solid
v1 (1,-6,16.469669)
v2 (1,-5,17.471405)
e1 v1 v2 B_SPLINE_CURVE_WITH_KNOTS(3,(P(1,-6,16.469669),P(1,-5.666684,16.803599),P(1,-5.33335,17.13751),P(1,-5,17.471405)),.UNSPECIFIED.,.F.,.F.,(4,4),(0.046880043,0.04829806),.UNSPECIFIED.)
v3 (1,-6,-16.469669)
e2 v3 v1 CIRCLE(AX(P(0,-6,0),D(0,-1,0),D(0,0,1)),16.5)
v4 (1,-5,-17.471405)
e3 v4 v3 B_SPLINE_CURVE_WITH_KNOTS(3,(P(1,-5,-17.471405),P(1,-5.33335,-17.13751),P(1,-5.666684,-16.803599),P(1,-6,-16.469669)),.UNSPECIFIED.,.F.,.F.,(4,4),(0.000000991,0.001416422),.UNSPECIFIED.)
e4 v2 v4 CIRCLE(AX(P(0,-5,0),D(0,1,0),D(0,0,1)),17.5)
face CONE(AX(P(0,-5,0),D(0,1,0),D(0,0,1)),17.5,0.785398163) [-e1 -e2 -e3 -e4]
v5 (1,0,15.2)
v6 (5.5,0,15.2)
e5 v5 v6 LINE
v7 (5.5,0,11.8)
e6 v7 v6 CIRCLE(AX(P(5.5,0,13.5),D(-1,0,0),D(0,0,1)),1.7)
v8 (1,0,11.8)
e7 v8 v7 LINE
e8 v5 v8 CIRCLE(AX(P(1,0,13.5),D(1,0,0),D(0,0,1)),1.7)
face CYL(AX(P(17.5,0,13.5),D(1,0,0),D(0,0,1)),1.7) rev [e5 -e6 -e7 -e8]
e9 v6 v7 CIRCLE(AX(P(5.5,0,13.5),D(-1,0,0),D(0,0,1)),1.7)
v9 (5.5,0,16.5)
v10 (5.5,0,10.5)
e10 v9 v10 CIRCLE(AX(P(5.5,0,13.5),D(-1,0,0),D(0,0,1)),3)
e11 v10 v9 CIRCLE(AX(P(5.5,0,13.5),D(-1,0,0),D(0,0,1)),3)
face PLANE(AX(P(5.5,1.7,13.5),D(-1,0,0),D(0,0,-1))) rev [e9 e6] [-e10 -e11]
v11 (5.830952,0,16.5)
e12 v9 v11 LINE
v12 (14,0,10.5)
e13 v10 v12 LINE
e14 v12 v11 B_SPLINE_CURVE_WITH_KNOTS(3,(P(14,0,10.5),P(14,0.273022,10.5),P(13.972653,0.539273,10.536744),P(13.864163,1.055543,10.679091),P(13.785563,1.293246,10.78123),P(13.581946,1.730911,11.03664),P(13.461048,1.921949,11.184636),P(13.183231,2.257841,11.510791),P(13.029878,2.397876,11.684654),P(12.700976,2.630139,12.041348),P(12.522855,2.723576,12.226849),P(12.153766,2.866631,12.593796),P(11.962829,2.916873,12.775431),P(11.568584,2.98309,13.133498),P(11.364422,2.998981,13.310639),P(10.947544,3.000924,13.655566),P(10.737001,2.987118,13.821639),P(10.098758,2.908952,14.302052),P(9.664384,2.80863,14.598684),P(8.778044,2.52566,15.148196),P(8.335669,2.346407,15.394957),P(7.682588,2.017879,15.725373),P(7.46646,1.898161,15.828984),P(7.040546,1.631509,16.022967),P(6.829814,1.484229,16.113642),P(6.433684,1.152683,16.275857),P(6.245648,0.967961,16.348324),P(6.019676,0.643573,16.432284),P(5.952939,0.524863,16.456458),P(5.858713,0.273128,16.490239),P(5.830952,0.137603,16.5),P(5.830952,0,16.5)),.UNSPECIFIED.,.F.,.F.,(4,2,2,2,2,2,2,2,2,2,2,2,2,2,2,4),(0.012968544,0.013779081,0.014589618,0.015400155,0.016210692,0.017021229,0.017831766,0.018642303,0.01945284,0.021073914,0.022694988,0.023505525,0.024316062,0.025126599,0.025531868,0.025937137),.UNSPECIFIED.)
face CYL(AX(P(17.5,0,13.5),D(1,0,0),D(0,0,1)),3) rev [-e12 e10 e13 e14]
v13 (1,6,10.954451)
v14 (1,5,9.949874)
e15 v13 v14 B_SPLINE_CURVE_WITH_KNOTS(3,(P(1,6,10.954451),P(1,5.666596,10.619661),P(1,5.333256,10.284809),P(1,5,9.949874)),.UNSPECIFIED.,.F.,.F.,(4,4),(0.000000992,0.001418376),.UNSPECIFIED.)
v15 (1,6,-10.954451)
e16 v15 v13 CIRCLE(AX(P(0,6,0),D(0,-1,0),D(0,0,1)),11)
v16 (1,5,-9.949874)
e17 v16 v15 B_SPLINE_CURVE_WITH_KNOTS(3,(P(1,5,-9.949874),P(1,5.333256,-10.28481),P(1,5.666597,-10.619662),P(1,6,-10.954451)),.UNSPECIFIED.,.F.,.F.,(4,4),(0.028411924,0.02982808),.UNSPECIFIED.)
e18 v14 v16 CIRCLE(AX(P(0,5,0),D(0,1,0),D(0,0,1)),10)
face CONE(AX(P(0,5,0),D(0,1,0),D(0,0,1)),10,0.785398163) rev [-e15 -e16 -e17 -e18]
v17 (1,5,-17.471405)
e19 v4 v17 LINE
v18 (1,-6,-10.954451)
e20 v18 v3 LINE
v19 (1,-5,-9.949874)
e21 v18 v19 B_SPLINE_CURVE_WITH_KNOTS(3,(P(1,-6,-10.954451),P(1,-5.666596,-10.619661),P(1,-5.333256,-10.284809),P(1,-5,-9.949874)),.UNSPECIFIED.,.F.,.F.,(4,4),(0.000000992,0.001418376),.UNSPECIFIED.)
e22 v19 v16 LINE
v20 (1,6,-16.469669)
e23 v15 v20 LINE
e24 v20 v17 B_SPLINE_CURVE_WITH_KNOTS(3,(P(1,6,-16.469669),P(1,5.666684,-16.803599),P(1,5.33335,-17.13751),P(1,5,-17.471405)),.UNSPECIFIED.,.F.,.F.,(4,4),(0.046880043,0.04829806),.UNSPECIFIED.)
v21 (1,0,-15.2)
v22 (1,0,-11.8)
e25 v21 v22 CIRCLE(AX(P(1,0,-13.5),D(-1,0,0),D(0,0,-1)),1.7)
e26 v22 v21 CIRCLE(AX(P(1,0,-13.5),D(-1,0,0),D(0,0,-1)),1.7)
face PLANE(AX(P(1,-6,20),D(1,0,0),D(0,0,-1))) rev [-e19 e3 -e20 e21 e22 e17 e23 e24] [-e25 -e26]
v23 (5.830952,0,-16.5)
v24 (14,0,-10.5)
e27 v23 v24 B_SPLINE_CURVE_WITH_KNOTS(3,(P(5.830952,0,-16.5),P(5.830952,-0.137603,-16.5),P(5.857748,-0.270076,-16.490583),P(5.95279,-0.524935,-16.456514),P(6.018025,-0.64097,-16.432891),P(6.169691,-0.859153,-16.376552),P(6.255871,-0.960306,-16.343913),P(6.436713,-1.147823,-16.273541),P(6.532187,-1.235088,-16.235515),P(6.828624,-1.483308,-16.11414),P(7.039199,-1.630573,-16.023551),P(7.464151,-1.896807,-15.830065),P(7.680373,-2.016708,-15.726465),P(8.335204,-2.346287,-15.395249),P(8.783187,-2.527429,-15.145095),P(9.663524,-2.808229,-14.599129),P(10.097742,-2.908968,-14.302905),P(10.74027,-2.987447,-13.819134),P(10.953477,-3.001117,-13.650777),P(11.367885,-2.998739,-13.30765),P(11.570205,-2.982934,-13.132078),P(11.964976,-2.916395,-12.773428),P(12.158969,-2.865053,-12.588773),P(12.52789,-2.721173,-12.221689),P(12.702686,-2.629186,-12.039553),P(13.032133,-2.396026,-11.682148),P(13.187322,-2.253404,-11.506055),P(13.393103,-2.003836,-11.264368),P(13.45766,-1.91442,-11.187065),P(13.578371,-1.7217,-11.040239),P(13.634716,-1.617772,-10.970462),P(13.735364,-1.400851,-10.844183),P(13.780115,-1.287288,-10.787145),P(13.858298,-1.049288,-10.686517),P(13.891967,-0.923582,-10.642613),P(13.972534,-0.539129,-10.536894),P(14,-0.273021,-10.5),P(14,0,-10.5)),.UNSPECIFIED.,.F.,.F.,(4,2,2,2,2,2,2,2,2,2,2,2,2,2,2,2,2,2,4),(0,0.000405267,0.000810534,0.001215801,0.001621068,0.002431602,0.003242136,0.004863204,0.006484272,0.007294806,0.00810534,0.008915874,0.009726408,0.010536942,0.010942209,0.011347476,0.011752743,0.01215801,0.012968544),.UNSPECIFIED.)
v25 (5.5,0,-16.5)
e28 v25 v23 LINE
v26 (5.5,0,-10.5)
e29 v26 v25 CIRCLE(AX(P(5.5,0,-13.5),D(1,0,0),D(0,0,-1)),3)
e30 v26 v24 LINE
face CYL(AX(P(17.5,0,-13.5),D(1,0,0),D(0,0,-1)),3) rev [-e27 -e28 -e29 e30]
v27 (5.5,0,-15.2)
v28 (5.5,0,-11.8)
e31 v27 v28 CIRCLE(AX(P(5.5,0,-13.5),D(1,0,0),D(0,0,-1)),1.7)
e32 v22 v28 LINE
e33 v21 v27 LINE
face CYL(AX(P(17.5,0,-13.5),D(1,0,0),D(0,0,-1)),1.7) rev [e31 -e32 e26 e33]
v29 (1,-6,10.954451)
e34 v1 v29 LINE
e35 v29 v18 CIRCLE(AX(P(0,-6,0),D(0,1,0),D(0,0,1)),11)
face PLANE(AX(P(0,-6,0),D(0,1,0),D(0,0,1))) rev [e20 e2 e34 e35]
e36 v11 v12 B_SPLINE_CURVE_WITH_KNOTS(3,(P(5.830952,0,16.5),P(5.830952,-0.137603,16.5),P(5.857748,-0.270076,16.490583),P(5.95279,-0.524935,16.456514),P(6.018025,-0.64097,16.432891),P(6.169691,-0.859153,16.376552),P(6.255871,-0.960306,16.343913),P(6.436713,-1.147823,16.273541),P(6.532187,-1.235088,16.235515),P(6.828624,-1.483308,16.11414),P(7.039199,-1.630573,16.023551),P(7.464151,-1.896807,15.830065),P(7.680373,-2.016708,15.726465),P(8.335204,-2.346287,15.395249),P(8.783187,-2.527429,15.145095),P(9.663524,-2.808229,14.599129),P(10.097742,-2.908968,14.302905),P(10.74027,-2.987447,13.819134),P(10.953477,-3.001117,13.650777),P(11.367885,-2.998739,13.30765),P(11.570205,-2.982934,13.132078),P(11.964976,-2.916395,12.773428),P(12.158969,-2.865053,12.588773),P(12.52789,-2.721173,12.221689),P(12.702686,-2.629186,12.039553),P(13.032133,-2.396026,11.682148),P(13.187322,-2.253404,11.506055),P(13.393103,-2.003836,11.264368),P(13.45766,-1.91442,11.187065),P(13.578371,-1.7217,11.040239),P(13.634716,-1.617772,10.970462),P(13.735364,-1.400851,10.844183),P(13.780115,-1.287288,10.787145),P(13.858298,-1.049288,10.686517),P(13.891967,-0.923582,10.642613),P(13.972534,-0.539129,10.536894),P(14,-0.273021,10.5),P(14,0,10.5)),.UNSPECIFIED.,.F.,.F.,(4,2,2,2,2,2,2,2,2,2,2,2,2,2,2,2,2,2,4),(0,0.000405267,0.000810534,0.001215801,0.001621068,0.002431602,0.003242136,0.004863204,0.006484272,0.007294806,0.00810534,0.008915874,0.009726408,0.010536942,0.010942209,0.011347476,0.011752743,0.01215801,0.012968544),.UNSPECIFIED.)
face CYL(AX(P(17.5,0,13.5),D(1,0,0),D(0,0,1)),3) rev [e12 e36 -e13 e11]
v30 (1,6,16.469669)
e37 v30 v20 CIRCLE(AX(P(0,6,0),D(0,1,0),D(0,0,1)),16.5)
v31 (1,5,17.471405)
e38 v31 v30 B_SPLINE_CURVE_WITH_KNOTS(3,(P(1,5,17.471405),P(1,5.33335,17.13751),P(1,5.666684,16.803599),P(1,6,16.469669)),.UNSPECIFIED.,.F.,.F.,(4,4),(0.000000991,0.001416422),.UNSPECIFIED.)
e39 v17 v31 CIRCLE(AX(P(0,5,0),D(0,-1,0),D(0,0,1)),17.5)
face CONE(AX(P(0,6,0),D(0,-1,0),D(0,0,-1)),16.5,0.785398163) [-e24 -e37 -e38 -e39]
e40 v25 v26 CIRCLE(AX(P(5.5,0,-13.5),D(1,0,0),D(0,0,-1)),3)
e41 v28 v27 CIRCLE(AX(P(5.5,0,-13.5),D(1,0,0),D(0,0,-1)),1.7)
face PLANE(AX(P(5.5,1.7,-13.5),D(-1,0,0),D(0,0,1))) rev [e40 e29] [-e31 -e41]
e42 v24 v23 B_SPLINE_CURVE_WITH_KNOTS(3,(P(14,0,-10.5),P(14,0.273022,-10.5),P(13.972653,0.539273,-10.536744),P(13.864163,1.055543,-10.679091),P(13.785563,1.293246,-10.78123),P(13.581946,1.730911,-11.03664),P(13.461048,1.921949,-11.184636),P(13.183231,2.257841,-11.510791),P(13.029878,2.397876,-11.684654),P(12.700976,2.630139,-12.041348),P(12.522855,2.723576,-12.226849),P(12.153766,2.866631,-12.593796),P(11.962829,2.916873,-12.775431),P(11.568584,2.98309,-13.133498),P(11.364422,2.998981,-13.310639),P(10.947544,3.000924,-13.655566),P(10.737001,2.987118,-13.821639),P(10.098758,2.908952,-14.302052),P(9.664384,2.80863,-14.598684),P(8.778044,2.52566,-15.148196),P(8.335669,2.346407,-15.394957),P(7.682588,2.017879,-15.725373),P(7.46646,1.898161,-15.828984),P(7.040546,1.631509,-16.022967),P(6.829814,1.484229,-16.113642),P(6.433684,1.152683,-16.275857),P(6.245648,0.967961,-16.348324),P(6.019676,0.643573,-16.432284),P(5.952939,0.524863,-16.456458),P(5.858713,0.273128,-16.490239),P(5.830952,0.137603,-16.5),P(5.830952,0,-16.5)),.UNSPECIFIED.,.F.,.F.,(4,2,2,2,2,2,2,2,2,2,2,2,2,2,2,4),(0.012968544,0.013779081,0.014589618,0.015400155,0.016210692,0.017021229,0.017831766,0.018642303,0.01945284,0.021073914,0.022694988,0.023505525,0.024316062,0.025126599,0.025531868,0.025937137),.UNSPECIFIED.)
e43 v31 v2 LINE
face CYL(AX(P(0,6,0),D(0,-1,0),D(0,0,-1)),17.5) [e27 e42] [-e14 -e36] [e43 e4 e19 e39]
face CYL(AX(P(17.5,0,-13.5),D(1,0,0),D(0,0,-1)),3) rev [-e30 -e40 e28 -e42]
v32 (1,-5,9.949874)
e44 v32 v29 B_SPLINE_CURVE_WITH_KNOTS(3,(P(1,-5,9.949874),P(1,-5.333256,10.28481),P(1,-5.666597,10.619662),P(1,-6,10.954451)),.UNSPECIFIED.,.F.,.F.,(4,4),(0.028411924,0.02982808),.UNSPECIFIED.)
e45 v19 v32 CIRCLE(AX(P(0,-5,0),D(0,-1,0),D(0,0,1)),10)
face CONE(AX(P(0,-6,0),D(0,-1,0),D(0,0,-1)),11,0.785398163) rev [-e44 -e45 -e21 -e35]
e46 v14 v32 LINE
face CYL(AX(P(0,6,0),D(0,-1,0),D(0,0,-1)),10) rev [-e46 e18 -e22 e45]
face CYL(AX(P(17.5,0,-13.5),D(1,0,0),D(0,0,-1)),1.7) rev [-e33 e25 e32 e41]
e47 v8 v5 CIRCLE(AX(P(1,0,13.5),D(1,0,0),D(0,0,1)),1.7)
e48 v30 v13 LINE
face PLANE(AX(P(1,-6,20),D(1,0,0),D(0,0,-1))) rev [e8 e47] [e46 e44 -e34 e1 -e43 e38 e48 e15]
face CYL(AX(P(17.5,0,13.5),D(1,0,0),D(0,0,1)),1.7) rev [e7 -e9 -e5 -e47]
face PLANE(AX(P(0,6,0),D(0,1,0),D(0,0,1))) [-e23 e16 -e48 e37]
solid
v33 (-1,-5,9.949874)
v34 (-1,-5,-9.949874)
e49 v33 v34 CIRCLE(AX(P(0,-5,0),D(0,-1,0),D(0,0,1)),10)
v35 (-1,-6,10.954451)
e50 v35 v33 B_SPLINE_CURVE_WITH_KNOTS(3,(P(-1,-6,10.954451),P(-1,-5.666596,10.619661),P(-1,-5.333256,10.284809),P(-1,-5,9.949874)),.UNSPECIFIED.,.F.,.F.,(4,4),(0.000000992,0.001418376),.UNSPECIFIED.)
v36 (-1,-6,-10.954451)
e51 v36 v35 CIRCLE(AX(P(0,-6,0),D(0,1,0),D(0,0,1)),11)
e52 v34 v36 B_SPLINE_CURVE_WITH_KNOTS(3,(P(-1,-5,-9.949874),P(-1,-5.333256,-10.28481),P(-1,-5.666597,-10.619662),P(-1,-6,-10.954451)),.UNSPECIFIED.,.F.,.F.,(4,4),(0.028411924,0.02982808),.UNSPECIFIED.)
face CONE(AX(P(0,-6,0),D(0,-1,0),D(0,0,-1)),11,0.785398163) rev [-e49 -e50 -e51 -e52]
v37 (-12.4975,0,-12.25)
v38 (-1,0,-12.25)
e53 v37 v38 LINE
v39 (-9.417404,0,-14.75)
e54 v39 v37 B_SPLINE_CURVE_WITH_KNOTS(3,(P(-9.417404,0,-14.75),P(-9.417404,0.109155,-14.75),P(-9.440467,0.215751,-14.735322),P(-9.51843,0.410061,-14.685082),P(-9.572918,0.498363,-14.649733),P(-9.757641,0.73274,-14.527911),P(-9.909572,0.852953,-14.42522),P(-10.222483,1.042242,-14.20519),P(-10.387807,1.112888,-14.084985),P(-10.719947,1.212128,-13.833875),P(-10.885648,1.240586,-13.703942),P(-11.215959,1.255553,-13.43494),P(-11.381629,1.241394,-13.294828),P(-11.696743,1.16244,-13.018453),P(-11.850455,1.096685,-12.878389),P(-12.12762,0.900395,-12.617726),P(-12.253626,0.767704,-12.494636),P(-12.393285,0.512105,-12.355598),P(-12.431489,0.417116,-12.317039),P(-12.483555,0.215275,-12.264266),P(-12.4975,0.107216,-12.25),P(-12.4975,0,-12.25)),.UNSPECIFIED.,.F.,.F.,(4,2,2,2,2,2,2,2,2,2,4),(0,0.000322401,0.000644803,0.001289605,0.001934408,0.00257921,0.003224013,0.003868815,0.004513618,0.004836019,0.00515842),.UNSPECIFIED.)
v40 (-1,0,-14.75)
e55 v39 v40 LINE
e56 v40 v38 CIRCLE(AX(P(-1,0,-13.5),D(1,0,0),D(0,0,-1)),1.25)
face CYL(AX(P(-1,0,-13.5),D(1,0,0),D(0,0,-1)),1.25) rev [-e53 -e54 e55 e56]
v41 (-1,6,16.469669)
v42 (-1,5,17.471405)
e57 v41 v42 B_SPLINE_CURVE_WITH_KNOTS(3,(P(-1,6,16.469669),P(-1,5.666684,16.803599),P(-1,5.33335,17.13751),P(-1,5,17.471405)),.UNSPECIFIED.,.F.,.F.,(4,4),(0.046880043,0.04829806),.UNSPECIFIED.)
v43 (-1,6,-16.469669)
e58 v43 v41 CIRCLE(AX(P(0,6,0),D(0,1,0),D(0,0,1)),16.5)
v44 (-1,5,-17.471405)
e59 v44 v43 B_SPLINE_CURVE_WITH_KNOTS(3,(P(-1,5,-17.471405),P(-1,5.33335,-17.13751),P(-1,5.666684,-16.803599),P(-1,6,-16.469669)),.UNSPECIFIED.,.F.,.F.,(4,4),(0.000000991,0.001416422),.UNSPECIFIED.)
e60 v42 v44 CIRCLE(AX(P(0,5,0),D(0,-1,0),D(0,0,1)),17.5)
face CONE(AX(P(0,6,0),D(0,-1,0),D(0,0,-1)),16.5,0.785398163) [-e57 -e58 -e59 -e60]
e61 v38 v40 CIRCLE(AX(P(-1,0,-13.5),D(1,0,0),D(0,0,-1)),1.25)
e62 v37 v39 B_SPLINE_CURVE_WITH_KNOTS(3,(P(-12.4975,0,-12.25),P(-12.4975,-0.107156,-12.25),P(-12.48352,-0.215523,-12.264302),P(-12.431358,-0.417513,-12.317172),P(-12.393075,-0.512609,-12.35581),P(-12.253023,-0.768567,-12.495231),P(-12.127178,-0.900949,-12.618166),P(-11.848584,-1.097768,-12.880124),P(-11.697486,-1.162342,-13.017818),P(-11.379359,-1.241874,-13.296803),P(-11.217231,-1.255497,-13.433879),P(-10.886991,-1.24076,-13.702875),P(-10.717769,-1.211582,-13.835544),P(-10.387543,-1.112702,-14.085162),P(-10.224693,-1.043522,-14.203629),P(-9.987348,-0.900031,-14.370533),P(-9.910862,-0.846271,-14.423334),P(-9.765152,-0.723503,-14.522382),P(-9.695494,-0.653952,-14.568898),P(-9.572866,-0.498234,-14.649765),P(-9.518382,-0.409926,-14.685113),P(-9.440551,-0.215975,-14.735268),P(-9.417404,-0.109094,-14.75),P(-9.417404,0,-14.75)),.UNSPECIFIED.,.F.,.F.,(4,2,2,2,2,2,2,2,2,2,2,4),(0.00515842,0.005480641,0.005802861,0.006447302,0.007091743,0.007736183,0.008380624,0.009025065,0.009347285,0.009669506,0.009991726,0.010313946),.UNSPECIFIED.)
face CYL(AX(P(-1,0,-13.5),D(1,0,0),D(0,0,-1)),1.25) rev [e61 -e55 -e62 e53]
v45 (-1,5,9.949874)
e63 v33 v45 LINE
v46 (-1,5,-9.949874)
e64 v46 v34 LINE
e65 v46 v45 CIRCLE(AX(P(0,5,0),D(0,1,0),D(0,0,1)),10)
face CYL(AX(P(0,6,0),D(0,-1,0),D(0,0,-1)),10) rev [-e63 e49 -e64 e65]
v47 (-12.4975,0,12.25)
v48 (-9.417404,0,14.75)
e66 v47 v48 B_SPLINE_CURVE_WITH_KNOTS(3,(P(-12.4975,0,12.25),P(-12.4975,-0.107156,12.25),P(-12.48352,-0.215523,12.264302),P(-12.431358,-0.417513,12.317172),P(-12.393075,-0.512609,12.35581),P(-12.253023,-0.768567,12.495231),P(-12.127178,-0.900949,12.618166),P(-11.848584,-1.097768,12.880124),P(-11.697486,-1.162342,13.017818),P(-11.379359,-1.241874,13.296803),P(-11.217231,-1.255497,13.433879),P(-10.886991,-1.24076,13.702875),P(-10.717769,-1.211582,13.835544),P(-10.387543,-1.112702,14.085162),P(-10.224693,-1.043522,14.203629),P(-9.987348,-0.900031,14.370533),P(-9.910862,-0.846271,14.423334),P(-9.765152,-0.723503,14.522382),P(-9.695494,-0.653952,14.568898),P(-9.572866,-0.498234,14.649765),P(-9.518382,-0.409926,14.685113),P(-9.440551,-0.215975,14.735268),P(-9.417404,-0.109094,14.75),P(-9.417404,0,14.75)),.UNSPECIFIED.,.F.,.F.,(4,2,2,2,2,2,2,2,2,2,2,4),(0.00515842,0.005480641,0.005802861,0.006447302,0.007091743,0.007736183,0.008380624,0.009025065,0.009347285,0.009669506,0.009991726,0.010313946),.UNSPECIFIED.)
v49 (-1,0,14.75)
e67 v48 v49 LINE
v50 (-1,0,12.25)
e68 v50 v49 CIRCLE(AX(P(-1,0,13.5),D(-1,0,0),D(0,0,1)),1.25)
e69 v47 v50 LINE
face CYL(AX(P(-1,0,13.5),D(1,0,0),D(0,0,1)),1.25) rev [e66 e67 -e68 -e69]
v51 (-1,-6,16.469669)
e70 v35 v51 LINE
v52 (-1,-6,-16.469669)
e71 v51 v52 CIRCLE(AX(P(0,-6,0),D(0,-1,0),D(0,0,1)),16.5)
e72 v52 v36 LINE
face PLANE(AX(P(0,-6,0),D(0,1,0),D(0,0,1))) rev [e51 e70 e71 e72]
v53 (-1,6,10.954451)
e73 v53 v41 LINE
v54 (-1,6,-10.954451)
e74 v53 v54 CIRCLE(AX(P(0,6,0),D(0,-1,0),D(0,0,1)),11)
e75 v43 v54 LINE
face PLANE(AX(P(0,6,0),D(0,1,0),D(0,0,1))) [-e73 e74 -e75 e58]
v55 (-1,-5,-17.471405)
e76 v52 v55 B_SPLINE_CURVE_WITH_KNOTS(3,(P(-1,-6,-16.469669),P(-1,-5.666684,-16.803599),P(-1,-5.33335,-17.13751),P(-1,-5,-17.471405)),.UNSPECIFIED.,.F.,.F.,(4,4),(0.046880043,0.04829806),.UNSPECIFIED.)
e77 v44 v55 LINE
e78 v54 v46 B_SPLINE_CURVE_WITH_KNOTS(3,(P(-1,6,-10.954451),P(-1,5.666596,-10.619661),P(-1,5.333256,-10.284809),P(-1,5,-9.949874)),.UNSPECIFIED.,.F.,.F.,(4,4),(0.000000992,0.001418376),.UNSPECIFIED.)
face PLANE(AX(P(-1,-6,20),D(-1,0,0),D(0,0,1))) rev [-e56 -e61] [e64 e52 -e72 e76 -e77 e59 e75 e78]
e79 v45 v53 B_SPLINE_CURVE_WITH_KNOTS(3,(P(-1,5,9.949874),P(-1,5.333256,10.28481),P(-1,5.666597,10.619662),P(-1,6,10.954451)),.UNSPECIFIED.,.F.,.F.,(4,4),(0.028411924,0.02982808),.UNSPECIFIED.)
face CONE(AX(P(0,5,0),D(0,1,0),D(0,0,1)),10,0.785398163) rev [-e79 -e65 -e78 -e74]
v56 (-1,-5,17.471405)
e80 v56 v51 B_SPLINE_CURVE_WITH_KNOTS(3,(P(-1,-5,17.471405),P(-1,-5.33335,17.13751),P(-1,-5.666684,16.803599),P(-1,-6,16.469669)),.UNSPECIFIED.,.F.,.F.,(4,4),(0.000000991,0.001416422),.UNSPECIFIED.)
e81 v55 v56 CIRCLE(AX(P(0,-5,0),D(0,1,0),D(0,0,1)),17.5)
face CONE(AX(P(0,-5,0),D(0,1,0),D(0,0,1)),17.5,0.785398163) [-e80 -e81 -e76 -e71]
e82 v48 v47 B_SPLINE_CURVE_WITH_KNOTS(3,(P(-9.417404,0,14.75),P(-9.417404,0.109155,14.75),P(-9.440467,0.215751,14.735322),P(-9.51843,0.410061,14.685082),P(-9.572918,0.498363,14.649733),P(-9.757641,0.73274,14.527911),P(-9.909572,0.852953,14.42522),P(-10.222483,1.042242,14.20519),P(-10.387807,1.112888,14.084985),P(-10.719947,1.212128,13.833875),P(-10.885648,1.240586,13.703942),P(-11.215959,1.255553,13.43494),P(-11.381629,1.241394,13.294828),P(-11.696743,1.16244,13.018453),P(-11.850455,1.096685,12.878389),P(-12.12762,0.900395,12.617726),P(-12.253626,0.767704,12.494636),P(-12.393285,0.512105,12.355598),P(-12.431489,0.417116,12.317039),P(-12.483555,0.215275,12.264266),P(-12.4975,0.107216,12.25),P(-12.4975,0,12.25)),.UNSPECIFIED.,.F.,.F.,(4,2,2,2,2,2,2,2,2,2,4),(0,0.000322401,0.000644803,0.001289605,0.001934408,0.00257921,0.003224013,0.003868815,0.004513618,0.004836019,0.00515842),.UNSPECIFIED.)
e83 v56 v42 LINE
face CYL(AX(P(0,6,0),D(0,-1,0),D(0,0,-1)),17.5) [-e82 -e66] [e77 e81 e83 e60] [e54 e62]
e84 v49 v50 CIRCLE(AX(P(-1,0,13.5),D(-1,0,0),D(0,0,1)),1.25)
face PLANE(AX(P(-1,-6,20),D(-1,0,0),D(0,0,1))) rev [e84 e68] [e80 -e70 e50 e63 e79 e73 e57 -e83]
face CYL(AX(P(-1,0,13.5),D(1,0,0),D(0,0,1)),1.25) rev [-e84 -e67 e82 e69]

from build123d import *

# Parameters (mm, degrees)
SKETCH_1_R          = 17.5
SKETCH_1_R_2        = 10
EXTRUDE_1_DEPTH     = 6
CHAMFER_1_SIZE      = 1
SKETCH_2_W          = 2
SKETCH_2_H          = 40
CUT_EXTRUDE_1_DEPTH = 28.504545079
SKETCH_11_W         = 1.25
SKETCH_11_H         = 16.5


with BuildPart() as part:
    # 草图1 → 凸台-拉伸1 (new, symmetric)
    with BuildSketch(Plane(origin=(0, 0, 0), x_dir=(1, 0, 0), z_dir=(0, 1, 0))):
        with Locations(Location((0, 0, 0), (0, 0, 270))):
            Circle(SKETCH_1_R)
        with Locations(Location((0, 0, 0), (0, 0, 270))):
            Circle(SKETCH_1_R_2, mode=Mode.SUBTRACT)
    extrude(amount=EXTRUDE_1_DEPTH, both=True)

    # 倒角1
    chamfer_1_edges = [part.edges().sort_by_distance(p)[0] for p in [
        (0, -6, -17.5),
        (0, 6, -17.5),
        (0, -6, -10),
        (0, 6, -10),
    ]]
    chamfer(chamfer_1_edges, length=CHAMFER_1_SIZE)

    # 草图2 → 切除-拉伸1 (cut, through all)
    with BuildSketch(Plane(origin=(0, 6, 0), x_dir=(1, 0, 0), z_dir=(0, 1, 0))):
        Rectangle(SKETCH_2_W, SKETCH_2_H)
    extrude(amount=-CUT_EXTRUDE_1_DEPTH, mode=Mode.SUBTRACT)


with BuildPart() as cut_extrude_1_piece_1:
    # of the separate pieces the step leaves, piece 1, a body of its own (cut_extrude_1_pieces)
    add(part.part.solids().sort_by_distance((-1, -5, -17.47140521))[0])

    # 草图11 → Hole Wizard M3 _1 2 (revolve, cut)
    with BuildSketch(Plane(origin=(-1, 0, -13.5), x_dir=(0, 0, -1), z_dir=(0, 1, 0))):
        with Locations((0.625, 8.25)):
            Rectangle(SKETCH_11_W, SKETCH_11_H)
    hole_wizard_m3_1_2 = revolve(axis=Axis((5.35, 0, -13.5), (-1, 0, 0)), mode=Mode.SUBTRACT)


with BuildPart() as cut_extrude_1_piece_2:
    # of the separate pieces the step leaves, piece 2, a body of its own (cut_extrude_1_pieces)
    add(part.part.solids().sort_by_distance((1, -5, 17.47140521))[0])

    # 草图6 → Hole Wizard M3 _1 (revolve, cut)
    with BuildSketch(Plane(origin=(17.5, 0, -13.5), x_dir=(0, 0, -1), z_dir=(0, 1, 0))):
        Polygon((0, 0), (0, 17.521463052), (1.7, 16.5), (1.7, 12), (3, 12), (3, 0), align=None)
    hole_wizard_m3_1 = revolve(axis=Axis((23.85, 0, -13.5), (-1, 0, 0)), mode=Mode.SUBTRACT)


with BuildPart() as mirror_1_tool:
    # 镜向1: Hole Wizard M3 _1, Hole Wizard M3 _1 2 across plane
    add(hole_wizard_m3_1.mirror(Plane.XY))
    add(hole_wizard_m3_1_2.mirror(Plane.XY))


with BuildPart() as cut_extrude_1_piece_1_1:
    add(cut_extrude_1_piece_1.part)

    # 镜向1: cut by mirror_1_tool
    add(mirror_1_tool.part, mode=Mode.SUBTRACT)


with BuildPart() as cut_extrude_1_piece_2_1:
    add(cut_extrude_1_piece_2.part)

    # 镜向1: cut by mirror_1_tool
    add(mirror_1_tool.part, mode=Mode.SUBTRACT)


solid = Compound([cut_extrude_1_piece_1_1.part, cut_extrude_1_piece_2_1.part])
